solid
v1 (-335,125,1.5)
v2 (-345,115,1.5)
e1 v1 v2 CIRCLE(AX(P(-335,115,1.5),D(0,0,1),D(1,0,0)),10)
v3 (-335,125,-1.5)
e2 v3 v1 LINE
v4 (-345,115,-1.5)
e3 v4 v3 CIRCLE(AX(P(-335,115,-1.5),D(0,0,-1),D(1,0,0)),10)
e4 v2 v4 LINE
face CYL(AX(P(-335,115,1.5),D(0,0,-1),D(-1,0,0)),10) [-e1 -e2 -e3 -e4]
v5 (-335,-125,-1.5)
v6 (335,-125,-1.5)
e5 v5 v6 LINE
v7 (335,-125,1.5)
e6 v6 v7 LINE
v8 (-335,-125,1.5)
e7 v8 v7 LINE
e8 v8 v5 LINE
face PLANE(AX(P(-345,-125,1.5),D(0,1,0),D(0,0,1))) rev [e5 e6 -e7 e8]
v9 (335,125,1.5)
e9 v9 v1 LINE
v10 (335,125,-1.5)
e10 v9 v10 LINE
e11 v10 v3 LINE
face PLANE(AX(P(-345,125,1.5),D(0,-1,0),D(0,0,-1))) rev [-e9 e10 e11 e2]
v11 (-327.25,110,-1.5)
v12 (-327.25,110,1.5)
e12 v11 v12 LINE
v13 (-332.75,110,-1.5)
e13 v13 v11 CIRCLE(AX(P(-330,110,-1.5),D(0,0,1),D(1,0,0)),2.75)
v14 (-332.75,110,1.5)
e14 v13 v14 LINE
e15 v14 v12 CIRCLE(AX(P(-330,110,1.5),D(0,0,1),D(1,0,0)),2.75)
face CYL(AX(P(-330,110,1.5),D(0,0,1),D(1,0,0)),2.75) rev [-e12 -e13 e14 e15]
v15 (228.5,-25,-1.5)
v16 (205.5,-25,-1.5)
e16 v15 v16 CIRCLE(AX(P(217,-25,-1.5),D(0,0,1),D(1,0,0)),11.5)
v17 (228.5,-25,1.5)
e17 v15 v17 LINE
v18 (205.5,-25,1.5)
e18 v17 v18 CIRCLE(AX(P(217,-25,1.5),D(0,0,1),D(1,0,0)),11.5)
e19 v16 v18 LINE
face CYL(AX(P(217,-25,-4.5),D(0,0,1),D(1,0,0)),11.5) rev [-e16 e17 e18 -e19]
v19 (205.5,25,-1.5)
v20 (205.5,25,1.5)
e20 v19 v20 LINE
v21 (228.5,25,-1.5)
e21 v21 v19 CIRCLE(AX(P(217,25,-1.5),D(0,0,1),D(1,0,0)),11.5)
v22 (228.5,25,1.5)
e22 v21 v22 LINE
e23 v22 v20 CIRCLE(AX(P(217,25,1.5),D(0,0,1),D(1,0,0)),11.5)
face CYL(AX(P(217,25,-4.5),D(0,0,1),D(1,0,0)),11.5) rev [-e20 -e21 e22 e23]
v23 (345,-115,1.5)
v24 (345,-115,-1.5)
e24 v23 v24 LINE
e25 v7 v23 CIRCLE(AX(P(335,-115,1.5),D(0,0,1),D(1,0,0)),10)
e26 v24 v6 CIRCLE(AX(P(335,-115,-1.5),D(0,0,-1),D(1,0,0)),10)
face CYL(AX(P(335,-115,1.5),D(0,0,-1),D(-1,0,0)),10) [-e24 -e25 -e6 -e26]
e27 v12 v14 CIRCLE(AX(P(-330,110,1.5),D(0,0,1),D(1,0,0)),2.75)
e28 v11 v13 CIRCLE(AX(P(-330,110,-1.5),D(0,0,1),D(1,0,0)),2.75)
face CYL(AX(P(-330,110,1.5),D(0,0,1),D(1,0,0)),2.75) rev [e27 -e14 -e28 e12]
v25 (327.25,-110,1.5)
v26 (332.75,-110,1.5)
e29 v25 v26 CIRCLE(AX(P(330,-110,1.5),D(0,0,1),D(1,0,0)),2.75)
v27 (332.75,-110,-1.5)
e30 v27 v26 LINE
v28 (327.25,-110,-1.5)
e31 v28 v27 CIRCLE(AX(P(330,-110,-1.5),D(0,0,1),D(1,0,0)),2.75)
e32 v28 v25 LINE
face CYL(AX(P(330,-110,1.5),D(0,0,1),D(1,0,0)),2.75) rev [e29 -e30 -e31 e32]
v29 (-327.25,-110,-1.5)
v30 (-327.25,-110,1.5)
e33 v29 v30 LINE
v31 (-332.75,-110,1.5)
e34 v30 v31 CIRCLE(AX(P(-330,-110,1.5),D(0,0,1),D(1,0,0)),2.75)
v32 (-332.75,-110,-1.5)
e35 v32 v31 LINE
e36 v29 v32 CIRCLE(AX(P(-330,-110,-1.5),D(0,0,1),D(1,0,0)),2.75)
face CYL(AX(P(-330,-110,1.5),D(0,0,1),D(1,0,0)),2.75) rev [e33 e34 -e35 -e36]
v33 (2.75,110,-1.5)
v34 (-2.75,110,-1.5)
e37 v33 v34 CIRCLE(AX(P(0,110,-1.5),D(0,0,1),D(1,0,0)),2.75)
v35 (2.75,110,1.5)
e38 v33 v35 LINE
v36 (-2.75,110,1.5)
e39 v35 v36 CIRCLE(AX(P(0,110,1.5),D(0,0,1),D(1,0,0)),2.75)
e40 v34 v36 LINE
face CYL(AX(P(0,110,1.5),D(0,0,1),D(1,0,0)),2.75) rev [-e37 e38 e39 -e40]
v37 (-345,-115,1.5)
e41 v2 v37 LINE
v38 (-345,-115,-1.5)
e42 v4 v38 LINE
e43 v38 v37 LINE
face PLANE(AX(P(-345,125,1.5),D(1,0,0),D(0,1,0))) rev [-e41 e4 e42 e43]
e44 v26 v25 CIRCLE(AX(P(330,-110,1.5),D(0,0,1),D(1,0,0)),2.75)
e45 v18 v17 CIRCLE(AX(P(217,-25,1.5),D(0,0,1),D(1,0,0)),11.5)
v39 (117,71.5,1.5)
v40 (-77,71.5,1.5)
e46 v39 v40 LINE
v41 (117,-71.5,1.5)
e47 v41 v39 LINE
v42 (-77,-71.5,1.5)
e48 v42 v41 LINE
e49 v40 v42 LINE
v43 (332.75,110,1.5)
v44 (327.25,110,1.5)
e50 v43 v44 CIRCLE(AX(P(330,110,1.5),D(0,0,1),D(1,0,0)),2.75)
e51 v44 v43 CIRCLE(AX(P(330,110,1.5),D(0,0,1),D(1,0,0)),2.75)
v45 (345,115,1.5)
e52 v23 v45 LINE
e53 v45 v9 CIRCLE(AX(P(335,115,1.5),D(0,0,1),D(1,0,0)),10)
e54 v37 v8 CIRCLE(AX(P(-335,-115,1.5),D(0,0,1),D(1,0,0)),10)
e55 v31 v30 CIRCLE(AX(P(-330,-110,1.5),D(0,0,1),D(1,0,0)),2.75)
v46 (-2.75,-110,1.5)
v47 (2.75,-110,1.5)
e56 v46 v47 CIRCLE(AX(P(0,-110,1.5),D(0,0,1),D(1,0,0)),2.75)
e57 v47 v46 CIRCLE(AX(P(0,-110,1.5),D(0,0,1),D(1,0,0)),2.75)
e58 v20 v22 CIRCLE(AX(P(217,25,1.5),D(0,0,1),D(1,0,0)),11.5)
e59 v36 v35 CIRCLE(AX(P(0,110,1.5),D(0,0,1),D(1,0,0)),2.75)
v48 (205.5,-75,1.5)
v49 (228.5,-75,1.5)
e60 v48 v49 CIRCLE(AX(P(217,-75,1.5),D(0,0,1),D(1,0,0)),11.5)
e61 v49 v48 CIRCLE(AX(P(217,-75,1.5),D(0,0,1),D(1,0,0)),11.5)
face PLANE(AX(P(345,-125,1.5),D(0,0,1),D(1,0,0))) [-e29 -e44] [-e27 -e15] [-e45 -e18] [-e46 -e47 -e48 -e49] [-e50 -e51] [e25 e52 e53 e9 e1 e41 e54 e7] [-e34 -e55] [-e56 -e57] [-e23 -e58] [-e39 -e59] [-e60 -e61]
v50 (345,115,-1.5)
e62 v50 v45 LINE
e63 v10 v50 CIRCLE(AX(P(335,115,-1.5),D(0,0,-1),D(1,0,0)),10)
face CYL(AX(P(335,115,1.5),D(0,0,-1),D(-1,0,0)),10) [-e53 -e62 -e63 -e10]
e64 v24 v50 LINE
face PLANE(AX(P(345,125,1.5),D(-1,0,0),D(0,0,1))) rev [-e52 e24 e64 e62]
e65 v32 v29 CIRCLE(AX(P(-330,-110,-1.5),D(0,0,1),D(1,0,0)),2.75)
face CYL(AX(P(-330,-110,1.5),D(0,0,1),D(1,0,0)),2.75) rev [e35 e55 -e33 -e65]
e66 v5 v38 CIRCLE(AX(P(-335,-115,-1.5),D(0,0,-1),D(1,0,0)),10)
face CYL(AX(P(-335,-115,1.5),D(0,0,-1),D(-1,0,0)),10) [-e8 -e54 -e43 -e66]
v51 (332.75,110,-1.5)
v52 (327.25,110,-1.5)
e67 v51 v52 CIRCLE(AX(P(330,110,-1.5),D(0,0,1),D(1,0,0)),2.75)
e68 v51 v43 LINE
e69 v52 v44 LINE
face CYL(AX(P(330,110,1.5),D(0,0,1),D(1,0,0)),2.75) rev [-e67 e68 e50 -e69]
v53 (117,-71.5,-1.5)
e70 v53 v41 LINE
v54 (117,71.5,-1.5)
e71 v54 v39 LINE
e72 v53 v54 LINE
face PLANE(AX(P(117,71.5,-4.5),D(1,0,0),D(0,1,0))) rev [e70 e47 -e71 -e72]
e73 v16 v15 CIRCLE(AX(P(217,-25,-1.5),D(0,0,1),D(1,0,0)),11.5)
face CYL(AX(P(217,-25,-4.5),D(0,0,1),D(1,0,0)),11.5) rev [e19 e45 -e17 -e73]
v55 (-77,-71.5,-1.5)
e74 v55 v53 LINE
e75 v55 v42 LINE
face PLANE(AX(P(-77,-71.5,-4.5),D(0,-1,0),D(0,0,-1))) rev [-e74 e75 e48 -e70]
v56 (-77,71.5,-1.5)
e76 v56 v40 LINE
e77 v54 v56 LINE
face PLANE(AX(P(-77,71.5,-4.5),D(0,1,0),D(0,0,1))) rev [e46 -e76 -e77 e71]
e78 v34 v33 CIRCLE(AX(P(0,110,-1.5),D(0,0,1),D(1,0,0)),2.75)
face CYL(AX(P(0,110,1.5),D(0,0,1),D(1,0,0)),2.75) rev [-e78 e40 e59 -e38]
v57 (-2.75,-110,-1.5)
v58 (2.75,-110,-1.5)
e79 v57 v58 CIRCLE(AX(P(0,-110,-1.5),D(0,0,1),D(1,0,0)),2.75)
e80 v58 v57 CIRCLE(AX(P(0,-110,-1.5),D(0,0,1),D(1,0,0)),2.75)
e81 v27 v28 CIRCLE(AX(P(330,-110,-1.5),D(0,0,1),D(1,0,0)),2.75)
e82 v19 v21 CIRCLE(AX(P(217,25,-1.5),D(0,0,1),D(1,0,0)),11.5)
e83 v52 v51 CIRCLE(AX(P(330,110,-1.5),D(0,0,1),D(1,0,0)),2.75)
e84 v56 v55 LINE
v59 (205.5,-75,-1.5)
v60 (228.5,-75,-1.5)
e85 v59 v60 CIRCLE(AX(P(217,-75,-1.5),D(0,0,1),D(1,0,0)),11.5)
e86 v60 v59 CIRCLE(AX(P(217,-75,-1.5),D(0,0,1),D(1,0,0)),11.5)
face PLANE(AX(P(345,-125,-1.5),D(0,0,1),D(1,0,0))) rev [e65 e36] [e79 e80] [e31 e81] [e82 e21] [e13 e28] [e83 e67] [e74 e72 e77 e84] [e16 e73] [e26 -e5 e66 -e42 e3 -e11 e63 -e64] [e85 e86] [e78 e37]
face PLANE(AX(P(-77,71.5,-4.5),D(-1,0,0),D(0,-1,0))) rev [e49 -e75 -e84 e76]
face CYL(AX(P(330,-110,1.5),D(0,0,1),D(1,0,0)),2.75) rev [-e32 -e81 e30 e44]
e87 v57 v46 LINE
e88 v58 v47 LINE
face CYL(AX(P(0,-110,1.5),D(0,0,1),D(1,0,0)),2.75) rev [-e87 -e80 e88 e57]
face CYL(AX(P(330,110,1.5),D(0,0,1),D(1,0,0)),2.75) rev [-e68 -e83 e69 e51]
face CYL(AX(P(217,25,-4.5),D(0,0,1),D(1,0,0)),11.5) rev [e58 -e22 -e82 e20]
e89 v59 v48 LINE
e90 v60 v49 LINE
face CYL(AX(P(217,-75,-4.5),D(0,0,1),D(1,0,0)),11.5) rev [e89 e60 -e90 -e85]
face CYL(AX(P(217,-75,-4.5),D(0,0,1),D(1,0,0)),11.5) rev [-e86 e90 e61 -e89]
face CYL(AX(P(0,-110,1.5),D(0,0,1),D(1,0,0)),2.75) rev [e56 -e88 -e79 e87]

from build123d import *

# Parameters (mm, degrees)
SKETCH_1_W                  = 690
SKETCH_1_H                  = 250
EXTRUDE_1_DEPTH             = 1.5
SKETCH_2_W                  = 194
SKETCH_2_H                  = 143
CUT_EXTRUDE_1_DEPTH         = 6
SKETCH_3_R                  = 11.5
CUT_EXTRUDE_2_DEPTH         = 6
FILLET_1_R                  = 10
HOLE_WIZARD_5_5_5_5_1_D     = 5.5
HOLE_WIZARD_5_5_5_5_1_DEPTH = 10
HOLE_WIZARD_5_5_5_5_1_TIP   = 1.652366702


with BuildPart() as part:
    # 草图1 → 凸台-拉伸1 (new, symmetric)
    with BuildSketch(Plane.XY):
        Rectangle(SKETCH_1_W, SKETCH_1_H)
    extrude(amount=EXTRUDE_1_DEPTH, both=True)

    # 草图2 → 切除-拉伸1 (cut)
    with BuildSketch(Plane.XY.offset(1.5)):
        with Locations((20, 0)):
            Rectangle(SKETCH_2_W, SKETCH_2_H)
    extrude(amount=-CUT_EXTRUDE_1_DEPTH, mode=Mode.SUBTRACT)

    # 草图3 → 切除-拉伸2 (cut)
    with BuildSketch(Plane.XY.offset(1.5)):
        with Locations((217, -25)):
            Circle(SKETCH_3_R)
        with Locations((217, -75)):
            Circle(SKETCH_3_R)
        with BuildLine():
            ThreePointArc((205.992928436, 28.33082206), (219.353810017, 13.74346508), (225.750187968, 32.462185372))
            ThreePointArc((225.750187968, 32.462185372), (214.646189983, 36.25653492), (205.992928436, 28.33082206))
        make_face()
    extrude(amount=-CUT_EXTRUDE_2_DEPTH, mode=Mode.SUBTRACT)

    # 圆角1
    fillet_1_edges = [part.edges().sort_by_distance(p)[0] for p in [
        (345, -125, 0),
        (-345, -125, 0),
        (-345, 125, 0),
        (345, 125, 0),
    ]]
    fillet(fillet_1_edges, radius=FILLET_1_R)

    # Ø5.5 (5.5) 直径孔1
    with Locations(Plane.XY.offset(1.5)):
        with Locations((-330, 110), (0, 110), (330, 110), (330, -110), (0, -110), (-330, -110)):
            Hole(HOLE_WIZARD_5_5_5_5_1_D / 2, depth=HOLE_WIZARD_5_5_5_5_1_DEPTH)
            with Locations((0, 0, -(HOLE_WIZARD_5_5_5_5_1_DEPTH + HOLE_WIZARD_5_5_5_5_1_TIP / 2))):  # 118° drill point
                Cone(0, HOLE_WIZARD_5_5_5_5_1_D / 2, HOLE_WIZARD_5_5_5_5_1_TIP, mode=Mode.SUBTRACT)


solid = part.part
